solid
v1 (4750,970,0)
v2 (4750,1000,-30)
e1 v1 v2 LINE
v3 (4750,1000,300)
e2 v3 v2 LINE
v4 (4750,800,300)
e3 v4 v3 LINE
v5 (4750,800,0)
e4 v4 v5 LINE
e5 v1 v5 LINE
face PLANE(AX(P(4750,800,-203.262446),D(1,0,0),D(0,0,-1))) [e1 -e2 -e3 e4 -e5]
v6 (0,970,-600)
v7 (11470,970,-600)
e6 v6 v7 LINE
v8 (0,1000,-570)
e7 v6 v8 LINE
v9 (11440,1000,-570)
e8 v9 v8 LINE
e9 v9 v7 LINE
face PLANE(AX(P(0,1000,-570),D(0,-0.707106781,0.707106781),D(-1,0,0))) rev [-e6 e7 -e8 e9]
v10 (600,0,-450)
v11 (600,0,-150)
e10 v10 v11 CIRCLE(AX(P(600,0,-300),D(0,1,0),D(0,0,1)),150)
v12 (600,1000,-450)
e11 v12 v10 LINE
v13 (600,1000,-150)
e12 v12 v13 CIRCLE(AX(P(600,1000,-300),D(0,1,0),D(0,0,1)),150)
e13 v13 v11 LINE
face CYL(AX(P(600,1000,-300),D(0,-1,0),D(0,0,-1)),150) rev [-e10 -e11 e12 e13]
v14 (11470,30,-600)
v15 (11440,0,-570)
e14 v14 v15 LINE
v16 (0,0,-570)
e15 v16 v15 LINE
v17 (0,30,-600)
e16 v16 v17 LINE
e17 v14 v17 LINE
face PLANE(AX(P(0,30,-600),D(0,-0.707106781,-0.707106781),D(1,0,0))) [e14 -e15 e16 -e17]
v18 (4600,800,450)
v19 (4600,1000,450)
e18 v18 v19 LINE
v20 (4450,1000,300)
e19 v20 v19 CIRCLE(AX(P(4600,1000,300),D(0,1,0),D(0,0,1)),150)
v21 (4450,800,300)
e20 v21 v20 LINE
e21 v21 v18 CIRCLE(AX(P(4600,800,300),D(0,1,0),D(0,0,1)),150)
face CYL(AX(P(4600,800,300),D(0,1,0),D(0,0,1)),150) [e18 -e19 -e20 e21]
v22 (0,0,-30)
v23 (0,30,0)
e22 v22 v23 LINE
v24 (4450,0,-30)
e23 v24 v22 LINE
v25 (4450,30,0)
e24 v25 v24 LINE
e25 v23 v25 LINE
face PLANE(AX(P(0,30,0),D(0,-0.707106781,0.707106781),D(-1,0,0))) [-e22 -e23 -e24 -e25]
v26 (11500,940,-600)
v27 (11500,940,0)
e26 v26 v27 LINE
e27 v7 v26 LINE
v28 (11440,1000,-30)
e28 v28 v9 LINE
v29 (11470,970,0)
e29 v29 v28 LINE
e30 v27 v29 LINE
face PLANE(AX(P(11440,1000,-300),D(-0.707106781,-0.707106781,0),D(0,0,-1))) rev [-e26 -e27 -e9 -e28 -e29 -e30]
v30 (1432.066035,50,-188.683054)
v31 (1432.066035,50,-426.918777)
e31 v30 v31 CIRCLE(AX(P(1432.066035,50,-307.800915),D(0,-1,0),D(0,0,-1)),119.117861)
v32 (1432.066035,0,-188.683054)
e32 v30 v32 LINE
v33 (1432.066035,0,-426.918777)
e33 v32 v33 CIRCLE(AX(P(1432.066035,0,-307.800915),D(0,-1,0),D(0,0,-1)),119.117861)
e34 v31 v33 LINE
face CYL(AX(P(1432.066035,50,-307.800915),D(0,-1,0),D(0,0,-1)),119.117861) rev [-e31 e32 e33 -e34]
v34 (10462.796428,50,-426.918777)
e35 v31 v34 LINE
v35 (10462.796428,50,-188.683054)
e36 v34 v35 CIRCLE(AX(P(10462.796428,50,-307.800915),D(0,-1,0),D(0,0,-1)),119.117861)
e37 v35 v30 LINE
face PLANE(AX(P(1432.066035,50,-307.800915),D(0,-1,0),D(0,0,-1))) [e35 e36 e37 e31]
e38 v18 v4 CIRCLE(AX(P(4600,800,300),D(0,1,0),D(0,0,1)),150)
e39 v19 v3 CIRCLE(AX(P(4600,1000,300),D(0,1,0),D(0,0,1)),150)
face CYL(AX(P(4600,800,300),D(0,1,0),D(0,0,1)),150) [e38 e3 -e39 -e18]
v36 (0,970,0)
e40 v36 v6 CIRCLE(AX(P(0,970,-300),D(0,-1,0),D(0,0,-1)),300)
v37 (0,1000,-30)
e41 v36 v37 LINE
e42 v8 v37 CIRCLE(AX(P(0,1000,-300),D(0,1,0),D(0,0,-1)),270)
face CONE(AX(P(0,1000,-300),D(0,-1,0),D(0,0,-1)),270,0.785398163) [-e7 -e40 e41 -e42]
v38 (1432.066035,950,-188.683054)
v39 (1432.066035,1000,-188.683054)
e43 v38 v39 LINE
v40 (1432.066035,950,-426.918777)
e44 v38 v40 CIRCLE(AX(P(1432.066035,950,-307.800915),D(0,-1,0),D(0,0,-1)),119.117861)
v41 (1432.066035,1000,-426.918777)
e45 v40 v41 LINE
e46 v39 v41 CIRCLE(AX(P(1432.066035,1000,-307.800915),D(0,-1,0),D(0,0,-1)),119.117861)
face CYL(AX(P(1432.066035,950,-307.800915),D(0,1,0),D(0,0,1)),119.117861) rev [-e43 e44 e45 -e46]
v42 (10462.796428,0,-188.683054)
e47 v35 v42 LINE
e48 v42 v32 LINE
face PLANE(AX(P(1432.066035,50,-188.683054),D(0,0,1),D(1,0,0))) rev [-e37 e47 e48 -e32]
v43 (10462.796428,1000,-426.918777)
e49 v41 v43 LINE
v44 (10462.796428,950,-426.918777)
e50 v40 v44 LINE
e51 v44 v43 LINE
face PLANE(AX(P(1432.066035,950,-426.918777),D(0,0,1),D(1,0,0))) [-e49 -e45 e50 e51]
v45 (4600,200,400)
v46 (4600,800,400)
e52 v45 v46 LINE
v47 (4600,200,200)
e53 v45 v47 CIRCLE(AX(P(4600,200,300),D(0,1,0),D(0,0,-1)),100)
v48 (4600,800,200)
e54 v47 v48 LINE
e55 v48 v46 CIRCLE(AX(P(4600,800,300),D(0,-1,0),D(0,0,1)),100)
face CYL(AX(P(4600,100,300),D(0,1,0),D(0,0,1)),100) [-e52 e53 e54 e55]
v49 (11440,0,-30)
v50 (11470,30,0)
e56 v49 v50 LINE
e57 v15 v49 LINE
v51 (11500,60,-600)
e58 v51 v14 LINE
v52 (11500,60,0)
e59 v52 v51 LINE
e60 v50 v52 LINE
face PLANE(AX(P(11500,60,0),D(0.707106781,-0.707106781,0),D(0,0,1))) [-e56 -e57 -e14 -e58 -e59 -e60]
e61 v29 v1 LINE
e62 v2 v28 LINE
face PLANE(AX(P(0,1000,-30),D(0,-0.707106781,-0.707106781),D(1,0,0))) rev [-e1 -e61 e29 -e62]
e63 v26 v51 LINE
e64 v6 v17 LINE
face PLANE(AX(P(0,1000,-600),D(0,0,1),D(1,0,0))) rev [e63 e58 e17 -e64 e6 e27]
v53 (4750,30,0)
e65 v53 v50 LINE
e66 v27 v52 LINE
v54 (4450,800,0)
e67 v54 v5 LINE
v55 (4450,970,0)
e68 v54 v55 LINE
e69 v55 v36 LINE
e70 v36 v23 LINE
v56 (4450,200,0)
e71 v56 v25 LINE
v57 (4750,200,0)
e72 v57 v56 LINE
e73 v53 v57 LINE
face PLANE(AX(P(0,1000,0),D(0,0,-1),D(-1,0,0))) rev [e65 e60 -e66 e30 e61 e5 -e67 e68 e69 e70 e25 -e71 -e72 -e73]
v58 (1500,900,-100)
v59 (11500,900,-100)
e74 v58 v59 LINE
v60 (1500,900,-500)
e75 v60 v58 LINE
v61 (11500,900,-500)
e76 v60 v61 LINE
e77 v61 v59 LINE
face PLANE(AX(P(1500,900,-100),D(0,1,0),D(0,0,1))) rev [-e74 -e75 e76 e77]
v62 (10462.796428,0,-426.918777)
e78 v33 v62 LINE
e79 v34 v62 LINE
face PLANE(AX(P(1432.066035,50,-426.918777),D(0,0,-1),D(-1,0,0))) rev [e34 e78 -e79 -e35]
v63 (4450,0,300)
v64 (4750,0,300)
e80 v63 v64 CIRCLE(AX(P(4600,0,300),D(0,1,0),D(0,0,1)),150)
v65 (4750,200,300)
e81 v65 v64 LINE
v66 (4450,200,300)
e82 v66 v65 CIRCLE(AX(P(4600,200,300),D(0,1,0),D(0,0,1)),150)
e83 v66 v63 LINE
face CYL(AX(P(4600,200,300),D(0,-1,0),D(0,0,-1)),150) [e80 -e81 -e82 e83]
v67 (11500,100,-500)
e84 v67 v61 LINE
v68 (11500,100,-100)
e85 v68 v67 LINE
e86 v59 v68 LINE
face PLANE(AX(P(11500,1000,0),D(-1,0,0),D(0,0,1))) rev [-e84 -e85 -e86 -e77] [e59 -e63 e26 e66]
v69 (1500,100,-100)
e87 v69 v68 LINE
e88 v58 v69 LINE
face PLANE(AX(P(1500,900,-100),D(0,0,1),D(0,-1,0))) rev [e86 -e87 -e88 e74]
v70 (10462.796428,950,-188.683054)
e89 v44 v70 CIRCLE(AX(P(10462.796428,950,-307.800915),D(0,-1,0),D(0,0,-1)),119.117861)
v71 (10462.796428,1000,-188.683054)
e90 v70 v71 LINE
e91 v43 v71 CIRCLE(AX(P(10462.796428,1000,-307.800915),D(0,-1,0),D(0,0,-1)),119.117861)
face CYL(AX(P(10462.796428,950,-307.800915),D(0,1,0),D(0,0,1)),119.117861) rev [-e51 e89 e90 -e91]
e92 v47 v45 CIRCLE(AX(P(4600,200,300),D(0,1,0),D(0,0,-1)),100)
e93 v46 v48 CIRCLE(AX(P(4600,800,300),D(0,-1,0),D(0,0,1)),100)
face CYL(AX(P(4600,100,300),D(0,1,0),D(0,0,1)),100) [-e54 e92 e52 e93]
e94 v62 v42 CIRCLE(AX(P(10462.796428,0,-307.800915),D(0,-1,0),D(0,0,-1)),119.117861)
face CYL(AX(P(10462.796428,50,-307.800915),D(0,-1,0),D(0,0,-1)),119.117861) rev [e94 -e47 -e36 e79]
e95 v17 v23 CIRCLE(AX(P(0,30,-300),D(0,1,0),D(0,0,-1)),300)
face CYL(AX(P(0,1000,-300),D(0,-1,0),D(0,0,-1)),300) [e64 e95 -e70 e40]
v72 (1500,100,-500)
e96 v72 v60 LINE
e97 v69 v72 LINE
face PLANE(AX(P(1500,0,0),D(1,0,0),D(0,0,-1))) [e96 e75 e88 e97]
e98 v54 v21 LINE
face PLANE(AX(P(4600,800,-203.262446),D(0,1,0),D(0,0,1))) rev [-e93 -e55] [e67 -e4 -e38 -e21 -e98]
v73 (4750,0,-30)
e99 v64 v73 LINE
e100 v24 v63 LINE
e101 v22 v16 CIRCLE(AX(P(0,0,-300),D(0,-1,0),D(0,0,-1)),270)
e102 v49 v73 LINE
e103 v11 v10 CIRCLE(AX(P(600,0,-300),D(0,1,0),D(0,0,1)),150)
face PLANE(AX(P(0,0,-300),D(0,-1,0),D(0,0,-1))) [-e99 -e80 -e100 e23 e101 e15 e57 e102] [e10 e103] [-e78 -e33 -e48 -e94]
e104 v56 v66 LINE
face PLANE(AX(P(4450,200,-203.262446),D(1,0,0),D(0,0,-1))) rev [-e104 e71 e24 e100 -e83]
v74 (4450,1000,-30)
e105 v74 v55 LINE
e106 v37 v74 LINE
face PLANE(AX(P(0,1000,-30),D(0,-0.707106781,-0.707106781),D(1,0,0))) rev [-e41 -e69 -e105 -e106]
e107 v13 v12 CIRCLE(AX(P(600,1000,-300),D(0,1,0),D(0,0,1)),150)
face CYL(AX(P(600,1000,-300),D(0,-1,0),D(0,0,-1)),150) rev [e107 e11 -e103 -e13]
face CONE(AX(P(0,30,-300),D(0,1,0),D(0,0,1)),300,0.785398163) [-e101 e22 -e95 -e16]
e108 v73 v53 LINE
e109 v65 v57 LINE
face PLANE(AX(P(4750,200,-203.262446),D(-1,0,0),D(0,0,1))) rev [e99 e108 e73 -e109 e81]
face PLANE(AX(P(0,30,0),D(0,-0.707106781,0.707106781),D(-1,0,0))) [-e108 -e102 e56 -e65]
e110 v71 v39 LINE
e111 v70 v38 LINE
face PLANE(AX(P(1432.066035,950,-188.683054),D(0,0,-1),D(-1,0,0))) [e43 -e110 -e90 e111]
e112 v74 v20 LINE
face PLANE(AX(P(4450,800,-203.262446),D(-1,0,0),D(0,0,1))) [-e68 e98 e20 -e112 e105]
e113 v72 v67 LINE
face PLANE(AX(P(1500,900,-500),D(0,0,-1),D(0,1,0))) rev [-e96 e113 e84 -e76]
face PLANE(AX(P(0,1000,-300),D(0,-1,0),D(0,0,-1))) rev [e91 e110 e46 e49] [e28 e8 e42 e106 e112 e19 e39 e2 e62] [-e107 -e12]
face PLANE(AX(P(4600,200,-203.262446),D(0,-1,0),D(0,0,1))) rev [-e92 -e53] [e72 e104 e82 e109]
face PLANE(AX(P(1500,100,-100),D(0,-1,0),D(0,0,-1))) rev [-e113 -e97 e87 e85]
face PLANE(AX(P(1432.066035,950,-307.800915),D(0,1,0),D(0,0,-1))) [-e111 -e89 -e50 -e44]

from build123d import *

# Parameters (mm, degrees)
SKETCH1_R           = 150
BOSS_EXTRUDE1_DEPTH = 1000
BOSS_EXTRUDE2_DEPTH = 200
SKETCH4_R           = 100
BOSS_EXTRUDE3_DEPTH = 700
SKETCH5_W           = 400
SKETCH5_H           = 800
CUT_EXTRUDE1_DEPTH  = 10000
CUT_EXTRUDE2_DEPTH  = 50
CHAMFER1_SIZE       = 30
CHAMFER2_SIZE       = 60


with BuildPart() as part:
    # Sketch1 → Boss-Extrude1 (new body)
    with BuildSketch(Plane(origin=(0, 0, 0), x_dir=(1, 0, 0), z_dir=(0, 1, 0))):
        with BuildLine():
            Line((0, 0), (11500, 0))
            Line((11500, 0), (11500, 600))
            Line((11500, 600), (694.445039307, 600))
            Line((694.445039307, 600), (0, 600))
            ThreePointArc((0, 600), (-300, 300), (0, 0))
        make_face()
        with Locations(Location((600, 300, 0), (0, 0, 270))):
            Circle(SKETCH1_R, mode=Mode.SUBTRACT)
    extrude(amount=BOSS_EXTRUDE1_DEPTH)

    # Sketch3 → Boss-Extrude2 (add)
    with BuildSketch(Plane(origin=(0, 1000, 0), x_dir=(1, 0, 0), z_dir=(0, 1, 0))):
        with BuildLine():
            Line((4750, 203.262446468), (4750, -300))
            ThreePointArc((4750, -300), (4600, -450), (4450, -300))
            Line((4450, -300), (4450, 203.262446468))
            ThreePointArc((4450, 203.262446468), (4600, 353.262446468), (4750, 203.262446468))
        make_face()
    boss_extrude2 = extrude(amount=-BOSS_EXTRUDE2_DEPTH)

    # Mirror1: Boss-Extrude2 across plane
    add(boss_extrude2.mirror(Plane.ZX.offset(500)))

    # Sketch4 → Boss-Extrude3 (add)
    with BuildSketch(Plane.XZ.offset(-800)):
        with Locations(Location((4600, 300, 0), (0, 0, 90))):
            Circle(SKETCH4_R)
    extrude(amount=BOSS_EXTRUDE3_DEPTH)

    # Sketch5 → Cut-Extrude1 (cut)
    with BuildSketch(Plane(origin=(11500, 0, 0), x_dir=(0, 0, -1), z_dir=(1, 0, 0))):
        with Locations((300, 500)):
            Rectangle(SKETCH5_W, SKETCH5_H)
    extrude(amount=-CUT_EXTRUDE1_DEPTH, mode=Mode.SUBTRACT)

    # Sketch6 → Cut-Extrude2 (cut)
    with BuildSketch(Plane.XZ):
        with BuildLine():
            Line((1432.066035129, -188.683053799), (10462.796428136, -188.683053799))
            ThreePointArc((10462.796428136, -188.683053799), (10581.914289518, -307.800915181), (10462.796428136, -426.918776563))
            Line((10462.796428136, -426.918776563), (1432.066035129, -426.918776563))
            ThreePointArc((1432.066035129, -426.918776563), (1312.948173747, -307.800915181), (1432.066035129, -188.683053799))
        make_face()
    cut_extrude2 = extrude(amount=-CUT_EXTRUDE2_DEPTH, mode=Mode.SUBTRACT)

    # Mirror2: Cut-Extrude2 across plane
    add(cut_extrude2.mirror(Plane.ZX.offset(500)), mode=Mode.SUBTRACT)

    # Chamfer1
    chamfer1_edges = [part.edges().sort_by_distance(p)[0] for p in [
        (5750, 1000, -600),
        (8125, 1000, 0),
        (8125, 0, 0),
        (-300, 1000, -300),
        (5750, 0, -600),
        (2225, 0, 0),
        (-300, 0, -300),
        (2225, 1000, 0),
    ]]
    chamfer(chamfer1_edges, length=CHAMFER1_SIZE)

    # Chamfer2
    chamfer2_edges = [part.edges().sort_by_distance(p)[0] for p in [
        (11500, 1000, -300),
        (11500, 0, -300),
    ]]
    chamfer(chamfer2_edges, length=CHAMFER2_SIZE)


solid = part.part
